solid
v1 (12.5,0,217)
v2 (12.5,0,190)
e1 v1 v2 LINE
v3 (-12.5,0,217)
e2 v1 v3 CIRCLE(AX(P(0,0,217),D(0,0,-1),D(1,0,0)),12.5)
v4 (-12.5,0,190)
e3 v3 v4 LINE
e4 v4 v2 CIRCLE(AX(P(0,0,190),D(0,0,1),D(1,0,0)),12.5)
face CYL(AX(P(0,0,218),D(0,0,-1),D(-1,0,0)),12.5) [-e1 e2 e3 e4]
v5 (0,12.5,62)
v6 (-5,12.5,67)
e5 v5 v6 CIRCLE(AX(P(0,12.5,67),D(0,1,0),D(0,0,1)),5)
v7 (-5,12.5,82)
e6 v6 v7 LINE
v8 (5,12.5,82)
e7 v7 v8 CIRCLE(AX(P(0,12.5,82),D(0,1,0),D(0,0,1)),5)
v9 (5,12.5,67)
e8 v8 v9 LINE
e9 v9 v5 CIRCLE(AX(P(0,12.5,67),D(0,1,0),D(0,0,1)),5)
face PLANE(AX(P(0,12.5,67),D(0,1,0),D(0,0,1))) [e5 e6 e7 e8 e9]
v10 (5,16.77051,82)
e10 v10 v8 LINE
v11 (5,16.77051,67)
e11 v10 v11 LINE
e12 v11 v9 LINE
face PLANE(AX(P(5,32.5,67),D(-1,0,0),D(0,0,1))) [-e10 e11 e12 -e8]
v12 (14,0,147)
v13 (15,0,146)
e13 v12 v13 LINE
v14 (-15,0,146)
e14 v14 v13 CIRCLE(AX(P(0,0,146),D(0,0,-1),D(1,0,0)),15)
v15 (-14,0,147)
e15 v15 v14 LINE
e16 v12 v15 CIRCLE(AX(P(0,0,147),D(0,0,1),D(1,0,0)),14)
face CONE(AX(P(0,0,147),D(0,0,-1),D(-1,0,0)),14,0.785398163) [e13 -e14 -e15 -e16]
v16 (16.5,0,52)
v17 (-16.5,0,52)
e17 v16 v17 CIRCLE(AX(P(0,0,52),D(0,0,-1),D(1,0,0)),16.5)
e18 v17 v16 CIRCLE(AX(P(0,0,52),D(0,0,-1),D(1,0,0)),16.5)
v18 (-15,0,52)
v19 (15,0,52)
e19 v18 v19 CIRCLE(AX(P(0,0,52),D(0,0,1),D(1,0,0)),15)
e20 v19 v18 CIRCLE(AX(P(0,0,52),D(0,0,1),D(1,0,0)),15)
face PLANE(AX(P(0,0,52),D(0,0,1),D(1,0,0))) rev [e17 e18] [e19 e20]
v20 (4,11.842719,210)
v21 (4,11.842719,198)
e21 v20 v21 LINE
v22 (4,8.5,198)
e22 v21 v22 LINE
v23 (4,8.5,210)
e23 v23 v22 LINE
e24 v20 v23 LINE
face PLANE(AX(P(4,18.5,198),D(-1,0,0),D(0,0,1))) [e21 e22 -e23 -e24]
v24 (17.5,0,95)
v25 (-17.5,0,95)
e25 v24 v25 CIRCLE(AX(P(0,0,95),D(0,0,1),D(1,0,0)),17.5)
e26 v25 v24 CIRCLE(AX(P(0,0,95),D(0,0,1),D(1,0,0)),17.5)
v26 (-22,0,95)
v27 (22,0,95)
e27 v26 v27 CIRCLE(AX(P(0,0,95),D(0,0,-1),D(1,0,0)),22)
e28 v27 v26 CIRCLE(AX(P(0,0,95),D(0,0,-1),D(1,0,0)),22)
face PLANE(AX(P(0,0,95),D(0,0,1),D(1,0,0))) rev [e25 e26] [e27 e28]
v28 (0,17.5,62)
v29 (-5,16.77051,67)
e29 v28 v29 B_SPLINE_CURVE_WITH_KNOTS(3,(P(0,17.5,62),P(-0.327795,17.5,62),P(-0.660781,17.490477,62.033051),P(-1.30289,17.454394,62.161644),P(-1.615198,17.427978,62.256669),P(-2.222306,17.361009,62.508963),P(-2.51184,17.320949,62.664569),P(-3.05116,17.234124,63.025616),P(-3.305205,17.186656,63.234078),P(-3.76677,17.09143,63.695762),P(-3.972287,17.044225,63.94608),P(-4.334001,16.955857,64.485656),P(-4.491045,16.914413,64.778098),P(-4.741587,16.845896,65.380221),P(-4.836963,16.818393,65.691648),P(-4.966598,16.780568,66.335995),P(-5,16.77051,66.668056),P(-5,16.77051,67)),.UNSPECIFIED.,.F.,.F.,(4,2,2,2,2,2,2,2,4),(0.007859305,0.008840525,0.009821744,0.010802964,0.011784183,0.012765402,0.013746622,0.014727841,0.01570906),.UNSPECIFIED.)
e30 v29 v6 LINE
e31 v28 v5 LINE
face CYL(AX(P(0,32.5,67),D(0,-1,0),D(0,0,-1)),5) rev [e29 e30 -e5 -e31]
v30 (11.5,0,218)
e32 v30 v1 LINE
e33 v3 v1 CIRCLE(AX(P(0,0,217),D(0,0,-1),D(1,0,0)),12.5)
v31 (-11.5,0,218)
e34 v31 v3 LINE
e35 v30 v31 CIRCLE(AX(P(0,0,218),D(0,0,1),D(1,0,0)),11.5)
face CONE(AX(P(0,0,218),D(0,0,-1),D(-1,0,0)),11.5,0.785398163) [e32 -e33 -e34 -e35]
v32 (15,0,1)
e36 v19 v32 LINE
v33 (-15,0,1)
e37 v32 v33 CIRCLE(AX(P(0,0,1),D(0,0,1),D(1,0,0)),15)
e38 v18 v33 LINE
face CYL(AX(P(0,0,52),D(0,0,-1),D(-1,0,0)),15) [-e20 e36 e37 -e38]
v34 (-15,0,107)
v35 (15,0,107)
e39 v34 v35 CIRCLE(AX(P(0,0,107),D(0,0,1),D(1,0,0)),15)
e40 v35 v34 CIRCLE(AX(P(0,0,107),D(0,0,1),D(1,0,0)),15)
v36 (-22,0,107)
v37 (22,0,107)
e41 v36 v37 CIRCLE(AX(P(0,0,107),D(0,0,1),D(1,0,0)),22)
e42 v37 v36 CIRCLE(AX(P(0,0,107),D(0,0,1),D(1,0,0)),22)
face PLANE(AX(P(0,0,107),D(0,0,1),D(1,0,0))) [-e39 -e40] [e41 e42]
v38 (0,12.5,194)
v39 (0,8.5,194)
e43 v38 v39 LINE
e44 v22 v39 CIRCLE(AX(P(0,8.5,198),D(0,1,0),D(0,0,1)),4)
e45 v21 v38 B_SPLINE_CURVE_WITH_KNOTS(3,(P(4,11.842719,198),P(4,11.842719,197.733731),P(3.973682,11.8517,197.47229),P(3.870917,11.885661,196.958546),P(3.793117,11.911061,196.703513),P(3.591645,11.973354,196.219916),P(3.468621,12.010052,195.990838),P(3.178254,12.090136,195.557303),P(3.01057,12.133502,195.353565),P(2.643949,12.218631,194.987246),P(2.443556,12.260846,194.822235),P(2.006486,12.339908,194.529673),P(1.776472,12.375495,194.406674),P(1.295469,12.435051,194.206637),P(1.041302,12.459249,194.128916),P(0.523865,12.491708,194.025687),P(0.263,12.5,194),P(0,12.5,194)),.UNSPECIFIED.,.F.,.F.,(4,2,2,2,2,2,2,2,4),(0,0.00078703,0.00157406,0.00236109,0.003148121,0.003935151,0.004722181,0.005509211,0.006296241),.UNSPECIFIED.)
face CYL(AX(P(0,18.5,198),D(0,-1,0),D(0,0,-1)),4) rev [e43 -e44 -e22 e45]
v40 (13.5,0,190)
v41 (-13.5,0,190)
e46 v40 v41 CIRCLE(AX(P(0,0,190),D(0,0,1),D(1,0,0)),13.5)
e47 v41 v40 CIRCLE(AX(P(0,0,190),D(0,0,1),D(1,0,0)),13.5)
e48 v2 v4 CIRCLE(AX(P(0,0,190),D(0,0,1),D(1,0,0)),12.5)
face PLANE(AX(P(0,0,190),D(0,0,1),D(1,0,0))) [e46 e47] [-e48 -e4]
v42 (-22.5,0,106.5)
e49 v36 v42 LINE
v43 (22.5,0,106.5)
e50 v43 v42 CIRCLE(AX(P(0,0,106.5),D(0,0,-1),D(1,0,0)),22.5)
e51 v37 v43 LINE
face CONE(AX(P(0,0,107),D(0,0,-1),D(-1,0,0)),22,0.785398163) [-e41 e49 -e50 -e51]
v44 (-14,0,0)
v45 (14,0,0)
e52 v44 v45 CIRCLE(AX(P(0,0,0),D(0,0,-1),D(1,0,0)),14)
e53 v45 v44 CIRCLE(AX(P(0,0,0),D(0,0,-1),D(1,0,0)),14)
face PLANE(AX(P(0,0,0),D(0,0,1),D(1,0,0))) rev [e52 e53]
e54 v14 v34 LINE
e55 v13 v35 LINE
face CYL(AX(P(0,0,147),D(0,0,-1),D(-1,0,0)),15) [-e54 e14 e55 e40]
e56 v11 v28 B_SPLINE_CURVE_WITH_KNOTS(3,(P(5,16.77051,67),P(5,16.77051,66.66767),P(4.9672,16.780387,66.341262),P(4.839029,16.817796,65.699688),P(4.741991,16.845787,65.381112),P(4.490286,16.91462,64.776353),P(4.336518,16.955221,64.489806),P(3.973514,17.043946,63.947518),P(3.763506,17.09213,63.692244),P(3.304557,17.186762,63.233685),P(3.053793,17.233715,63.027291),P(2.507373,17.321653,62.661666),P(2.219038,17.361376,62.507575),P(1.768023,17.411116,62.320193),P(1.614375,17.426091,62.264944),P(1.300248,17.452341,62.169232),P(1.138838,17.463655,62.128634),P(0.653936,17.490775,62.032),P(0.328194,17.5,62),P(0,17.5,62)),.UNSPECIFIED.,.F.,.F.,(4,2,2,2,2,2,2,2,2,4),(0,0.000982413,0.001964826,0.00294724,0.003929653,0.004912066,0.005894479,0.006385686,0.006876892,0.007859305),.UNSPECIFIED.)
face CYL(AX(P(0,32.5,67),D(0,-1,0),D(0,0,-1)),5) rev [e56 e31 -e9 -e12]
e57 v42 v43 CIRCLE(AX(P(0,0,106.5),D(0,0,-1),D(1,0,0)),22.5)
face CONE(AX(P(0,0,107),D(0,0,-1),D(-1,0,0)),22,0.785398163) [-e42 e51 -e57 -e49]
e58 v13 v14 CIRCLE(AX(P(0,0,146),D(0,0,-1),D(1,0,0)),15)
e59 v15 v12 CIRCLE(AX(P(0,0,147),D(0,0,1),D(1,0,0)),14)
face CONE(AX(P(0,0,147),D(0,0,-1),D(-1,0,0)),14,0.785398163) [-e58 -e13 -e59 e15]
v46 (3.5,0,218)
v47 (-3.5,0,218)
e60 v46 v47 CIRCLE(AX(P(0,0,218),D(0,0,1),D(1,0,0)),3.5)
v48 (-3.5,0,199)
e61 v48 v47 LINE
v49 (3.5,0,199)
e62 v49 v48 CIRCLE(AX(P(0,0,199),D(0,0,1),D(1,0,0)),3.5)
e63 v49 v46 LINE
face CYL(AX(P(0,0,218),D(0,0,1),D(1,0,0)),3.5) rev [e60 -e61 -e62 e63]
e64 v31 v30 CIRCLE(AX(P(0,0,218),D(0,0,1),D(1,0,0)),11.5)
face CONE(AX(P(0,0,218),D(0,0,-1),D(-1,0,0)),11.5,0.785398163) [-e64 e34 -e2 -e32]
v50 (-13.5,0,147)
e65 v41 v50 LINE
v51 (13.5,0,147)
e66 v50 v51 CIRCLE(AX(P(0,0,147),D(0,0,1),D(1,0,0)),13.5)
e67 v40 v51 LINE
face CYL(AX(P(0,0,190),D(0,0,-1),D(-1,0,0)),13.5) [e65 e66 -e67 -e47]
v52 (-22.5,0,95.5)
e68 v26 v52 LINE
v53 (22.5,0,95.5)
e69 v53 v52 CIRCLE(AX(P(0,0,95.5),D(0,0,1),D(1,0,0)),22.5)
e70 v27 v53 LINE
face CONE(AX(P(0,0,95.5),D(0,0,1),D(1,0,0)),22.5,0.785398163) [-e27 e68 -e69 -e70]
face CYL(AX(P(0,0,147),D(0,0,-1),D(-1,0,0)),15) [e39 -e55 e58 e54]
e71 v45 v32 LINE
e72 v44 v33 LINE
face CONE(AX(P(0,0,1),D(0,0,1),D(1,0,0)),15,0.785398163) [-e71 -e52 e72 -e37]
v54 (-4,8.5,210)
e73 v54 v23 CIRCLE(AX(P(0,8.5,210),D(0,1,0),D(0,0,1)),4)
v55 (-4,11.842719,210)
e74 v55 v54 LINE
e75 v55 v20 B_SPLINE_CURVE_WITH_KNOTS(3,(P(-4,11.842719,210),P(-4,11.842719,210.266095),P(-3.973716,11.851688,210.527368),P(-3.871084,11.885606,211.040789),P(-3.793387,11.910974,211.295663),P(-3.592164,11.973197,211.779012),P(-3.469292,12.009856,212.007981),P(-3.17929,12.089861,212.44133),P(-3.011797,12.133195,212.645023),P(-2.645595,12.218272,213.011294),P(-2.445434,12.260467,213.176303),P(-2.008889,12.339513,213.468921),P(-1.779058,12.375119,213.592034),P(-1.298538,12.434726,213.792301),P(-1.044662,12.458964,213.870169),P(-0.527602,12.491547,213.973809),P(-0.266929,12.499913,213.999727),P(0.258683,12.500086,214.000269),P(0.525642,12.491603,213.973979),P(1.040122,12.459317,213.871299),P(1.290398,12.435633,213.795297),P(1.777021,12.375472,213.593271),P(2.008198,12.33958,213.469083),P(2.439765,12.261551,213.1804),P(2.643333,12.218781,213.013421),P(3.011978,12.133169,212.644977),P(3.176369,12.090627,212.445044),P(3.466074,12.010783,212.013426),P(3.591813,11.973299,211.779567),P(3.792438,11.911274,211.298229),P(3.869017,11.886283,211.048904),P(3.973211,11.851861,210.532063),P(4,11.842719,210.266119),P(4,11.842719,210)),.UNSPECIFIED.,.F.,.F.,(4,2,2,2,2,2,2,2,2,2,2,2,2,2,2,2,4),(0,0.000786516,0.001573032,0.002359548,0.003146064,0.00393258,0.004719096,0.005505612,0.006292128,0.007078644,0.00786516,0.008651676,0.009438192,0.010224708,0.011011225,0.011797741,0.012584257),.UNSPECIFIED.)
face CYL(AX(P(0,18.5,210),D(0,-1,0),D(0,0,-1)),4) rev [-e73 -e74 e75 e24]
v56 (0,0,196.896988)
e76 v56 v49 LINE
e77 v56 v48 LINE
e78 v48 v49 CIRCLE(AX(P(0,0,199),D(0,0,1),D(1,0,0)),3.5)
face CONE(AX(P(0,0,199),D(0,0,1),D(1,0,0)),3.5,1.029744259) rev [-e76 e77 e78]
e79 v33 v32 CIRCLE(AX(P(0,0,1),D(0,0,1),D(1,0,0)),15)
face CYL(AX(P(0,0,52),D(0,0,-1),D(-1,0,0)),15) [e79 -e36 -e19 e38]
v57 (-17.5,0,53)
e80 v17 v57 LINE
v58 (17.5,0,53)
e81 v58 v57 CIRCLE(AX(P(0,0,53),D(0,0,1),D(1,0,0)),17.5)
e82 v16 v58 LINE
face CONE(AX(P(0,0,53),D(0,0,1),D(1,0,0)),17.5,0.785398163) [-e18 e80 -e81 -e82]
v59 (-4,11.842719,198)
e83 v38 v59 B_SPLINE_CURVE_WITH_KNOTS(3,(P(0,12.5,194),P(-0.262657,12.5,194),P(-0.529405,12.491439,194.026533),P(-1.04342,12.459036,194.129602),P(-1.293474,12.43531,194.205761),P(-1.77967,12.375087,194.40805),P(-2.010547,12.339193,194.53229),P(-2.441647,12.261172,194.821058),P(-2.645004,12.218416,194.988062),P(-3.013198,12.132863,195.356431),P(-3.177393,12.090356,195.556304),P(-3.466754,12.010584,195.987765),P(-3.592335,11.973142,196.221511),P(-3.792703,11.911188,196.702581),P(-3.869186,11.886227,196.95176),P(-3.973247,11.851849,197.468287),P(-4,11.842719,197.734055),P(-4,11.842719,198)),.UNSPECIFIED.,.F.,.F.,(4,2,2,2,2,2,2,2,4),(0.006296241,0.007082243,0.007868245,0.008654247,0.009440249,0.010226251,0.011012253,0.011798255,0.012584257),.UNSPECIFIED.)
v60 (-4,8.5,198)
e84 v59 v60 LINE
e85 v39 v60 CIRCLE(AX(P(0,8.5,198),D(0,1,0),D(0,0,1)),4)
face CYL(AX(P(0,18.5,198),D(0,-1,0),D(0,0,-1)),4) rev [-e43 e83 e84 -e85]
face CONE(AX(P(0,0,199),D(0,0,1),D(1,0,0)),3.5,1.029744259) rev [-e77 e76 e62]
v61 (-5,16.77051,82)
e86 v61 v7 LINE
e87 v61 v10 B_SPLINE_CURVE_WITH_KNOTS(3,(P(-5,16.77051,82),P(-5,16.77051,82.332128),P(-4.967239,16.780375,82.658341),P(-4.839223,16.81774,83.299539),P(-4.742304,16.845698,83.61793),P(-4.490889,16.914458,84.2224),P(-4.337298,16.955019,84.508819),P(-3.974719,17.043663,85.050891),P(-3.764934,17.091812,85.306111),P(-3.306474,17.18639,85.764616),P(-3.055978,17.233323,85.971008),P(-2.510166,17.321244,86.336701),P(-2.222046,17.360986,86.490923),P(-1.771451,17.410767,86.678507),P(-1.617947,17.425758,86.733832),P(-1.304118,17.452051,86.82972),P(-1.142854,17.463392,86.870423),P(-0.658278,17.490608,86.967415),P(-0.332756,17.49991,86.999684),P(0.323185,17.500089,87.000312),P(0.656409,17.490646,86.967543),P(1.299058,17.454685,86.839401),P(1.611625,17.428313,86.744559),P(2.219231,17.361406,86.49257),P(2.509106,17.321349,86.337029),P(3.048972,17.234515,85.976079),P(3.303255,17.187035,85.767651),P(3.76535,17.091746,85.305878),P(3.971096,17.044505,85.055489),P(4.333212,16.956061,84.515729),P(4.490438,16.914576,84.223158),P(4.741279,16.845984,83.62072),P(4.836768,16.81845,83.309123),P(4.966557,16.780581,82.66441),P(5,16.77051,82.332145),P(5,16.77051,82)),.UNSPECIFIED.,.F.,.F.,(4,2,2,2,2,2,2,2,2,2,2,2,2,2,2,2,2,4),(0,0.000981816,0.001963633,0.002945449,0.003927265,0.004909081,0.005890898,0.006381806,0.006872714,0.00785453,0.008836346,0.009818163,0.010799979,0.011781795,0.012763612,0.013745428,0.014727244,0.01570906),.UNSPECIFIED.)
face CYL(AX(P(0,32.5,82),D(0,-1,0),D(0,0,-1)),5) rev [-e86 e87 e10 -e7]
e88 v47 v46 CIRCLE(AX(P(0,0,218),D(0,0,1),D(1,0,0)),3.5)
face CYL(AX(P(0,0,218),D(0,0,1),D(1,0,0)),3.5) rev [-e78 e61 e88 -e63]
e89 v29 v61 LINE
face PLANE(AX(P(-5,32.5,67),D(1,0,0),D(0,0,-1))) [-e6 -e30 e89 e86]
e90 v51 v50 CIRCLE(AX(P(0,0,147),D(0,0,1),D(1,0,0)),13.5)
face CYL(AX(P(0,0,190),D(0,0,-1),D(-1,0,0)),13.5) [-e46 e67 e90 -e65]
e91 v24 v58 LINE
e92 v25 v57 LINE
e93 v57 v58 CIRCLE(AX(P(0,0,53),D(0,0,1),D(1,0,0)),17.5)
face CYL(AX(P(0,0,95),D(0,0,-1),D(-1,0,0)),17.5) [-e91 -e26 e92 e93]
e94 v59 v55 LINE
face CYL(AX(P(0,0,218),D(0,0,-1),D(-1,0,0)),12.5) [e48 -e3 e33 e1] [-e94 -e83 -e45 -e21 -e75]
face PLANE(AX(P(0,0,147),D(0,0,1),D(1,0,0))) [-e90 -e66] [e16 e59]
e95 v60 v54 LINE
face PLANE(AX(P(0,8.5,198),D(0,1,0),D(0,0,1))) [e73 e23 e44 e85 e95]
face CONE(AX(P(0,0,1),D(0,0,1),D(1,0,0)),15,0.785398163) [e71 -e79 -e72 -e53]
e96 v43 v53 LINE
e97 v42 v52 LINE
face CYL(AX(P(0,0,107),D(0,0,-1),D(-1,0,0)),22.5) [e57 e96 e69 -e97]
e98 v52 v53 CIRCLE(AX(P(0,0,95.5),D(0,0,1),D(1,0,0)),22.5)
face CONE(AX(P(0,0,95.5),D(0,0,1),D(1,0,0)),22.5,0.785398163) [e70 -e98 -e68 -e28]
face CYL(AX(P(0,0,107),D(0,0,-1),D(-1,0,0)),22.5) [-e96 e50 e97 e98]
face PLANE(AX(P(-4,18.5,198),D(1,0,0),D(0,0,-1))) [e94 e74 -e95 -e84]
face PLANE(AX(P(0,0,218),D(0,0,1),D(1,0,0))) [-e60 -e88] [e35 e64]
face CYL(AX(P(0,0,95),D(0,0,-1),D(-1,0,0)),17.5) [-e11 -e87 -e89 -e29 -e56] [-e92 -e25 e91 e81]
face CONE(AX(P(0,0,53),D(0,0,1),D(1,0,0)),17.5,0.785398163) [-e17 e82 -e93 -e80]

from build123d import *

# Parameters (mm, degrees)
SKETCH1_R                 = 15
BOSS_EXTRUDE1_DEPTH       = 52
SKETCH2_R                 = 17.5
BOSS_EXTRUDE2_DEPTH       = 43
SKETCH3_R                 = 22.5
BOSS_EXTRUDE3_DEPTH       = 12
SKETCH4_R                 = 15
BOSS_EXTRUDE4_DEPTH       = 40
SKETCH5_R                 = 13.5
BOSS_EXTRUDE5_DEPTH       = 43
SKETCH6_R                 = 12.5
BOSS_EXTRUDE6_DEPTH       = 28
CHAMFER1_SIZE             = 1
CHAMFER2_SIZE             = 1
CHAMFER3_SIZE             = 0.5
CUT_EXTRUDE1_START        = 12.5
CUT_EXTRUDE1_DEPTH        = 20
CUT_EXTRUDE2_START        = 8.5
CUT_EXTRUDE2_DEPTH        = 10
M8X1_0_TAPPED_HOLE1_D     = 7
M8X1_0_TAPPED_HOLE1_DEPTH = 19
M8X1_0_TAPPED_HOLE1_TIP   = 2.103012167


with BuildPart() as part:
    # Sketch1 → Boss-Extrude1 (new body)
    with BuildSketch(Plane.XY):
        with Locations(Location((0, 0, 0), (0, 0, 180))):
            Circle(SKETCH1_R)
    extrude(amount=BOSS_EXTRUDE1_DEPTH)

    # Sketch2 → Boss-Extrude2 (add)
    with BuildSketch(Plane.XY.offset(52)):
        Circle(SKETCH2_R)
    extrude(amount=BOSS_EXTRUDE2_DEPTH)

    # Sketch3 → Boss-Extrude3 (add)
    with BuildSketch(Plane.XY.offset(95)):
        Circle(SKETCH3_R)
    extrude(amount=BOSS_EXTRUDE3_DEPTH)

    # Sketch4 → Boss-Extrude4 (add)
    with BuildSketch(Plane.XY.offset(107)):
        with Locations(Location((0, 0, 0), (0, 0, 180))):
            Circle(SKETCH4_R)
    extrude(amount=BOSS_EXTRUDE4_DEPTH)

    # Sketch5 → Boss-Extrude5 (add)
    with BuildSketch(Plane.XY.offset(147)):
        Circle(SKETCH5_R)
    extrude(amount=BOSS_EXTRUDE5_DEPTH)

    # Sketch6 → Boss-Extrude6 (add)
    with BuildSketch(Plane.XY.offset(190)):
        Circle(SKETCH6_R)
    extrude(amount=BOSS_EXTRUDE6_DEPTH)

    # Chamfer1
    chamfer1_edges = [part.edges().sort_by_distance(p)[0] for p in [
        (15, 0, 0),
    ]]
    chamfer(chamfer1_edges, length=CHAMFER1_SIZE)

    # Chamfer2
    chamfer2_edges = [part.edges().sort_by_distance(p)[0] for p in [
        (15, 0, 147),
        (-12.5, 0, 218),
        (-17.5, 0, 52),
    ]]
    chamfer(chamfer2_edges, length=CHAMFER2_SIZE)

    # Chamfer3
    chamfer3_edges = [part.edges().sort_by_distance(p)[0] for p in [
        (-22.5, 0, 95),
        (-22.5, 0, 107),
    ]]
    chamfer(chamfer3_edges, length=CHAMFER3_SIZE)

    # Sketch7 → Cut-Extrude1 (cut)
    with BuildSketch(Plane(origin=(0, 0, 0), x_dir=(1, 0, 0), z_dir=(0, 1, 0)).offset(CUT_EXTRUDE1_START)):
        with BuildLine():
            Line((5, -67), (5, -82))
            ThreePointArc((5, -82), (0, -87), (-5, -82))
            Line((-5, -82), (-5, -67))
            ThreePointArc((-5, -67), (0, -62), (5, -67))
        make_face()
    extrude(amount=CUT_EXTRUDE1_DEPTH, mode=Mode.SUBTRACT)

    # Sketch8 → Cut-Extrude2 (cut)
    with BuildSketch(Plane(origin=(0, 0, 0), x_dir=(1, 0, 0), z_dir=(0, 1, 0)).offset(CUT_EXTRUDE2_START)):
        with BuildLine():
            Line((4, -198), (4, -210))
            ThreePointArc((4, -210), (0, -214), (-4, -210))
            Line((-4, -210), (-4, -198))
            ThreePointArc((-4, -198), (0, -194), (4, -198))
        make_face()
    extrude(amount=CUT_EXTRUDE2_DEPTH, mode=Mode.SUBTRACT)

    # M8x1.0 Tapped Hole1
    with Locations(Plane.XY.offset(218)):
        with Locations((0, 0)):
            Hole(M8X1_0_TAPPED_HOLE1_D / 2, depth=M8X1_0_TAPPED_HOLE1_DEPTH)
            with Locations((0, 0, -(M8X1_0_TAPPED_HOLE1_DEPTH + M8X1_0_TAPPED_HOLE1_TIP / 2))):  # 118° drill point
                Cone(0, M8X1_0_TAPPED_HOLE1_D / 2, M8X1_0_TAPPED_HOLE1_TIP, mode=Mode.SUBTRACT)


solid = part.part
